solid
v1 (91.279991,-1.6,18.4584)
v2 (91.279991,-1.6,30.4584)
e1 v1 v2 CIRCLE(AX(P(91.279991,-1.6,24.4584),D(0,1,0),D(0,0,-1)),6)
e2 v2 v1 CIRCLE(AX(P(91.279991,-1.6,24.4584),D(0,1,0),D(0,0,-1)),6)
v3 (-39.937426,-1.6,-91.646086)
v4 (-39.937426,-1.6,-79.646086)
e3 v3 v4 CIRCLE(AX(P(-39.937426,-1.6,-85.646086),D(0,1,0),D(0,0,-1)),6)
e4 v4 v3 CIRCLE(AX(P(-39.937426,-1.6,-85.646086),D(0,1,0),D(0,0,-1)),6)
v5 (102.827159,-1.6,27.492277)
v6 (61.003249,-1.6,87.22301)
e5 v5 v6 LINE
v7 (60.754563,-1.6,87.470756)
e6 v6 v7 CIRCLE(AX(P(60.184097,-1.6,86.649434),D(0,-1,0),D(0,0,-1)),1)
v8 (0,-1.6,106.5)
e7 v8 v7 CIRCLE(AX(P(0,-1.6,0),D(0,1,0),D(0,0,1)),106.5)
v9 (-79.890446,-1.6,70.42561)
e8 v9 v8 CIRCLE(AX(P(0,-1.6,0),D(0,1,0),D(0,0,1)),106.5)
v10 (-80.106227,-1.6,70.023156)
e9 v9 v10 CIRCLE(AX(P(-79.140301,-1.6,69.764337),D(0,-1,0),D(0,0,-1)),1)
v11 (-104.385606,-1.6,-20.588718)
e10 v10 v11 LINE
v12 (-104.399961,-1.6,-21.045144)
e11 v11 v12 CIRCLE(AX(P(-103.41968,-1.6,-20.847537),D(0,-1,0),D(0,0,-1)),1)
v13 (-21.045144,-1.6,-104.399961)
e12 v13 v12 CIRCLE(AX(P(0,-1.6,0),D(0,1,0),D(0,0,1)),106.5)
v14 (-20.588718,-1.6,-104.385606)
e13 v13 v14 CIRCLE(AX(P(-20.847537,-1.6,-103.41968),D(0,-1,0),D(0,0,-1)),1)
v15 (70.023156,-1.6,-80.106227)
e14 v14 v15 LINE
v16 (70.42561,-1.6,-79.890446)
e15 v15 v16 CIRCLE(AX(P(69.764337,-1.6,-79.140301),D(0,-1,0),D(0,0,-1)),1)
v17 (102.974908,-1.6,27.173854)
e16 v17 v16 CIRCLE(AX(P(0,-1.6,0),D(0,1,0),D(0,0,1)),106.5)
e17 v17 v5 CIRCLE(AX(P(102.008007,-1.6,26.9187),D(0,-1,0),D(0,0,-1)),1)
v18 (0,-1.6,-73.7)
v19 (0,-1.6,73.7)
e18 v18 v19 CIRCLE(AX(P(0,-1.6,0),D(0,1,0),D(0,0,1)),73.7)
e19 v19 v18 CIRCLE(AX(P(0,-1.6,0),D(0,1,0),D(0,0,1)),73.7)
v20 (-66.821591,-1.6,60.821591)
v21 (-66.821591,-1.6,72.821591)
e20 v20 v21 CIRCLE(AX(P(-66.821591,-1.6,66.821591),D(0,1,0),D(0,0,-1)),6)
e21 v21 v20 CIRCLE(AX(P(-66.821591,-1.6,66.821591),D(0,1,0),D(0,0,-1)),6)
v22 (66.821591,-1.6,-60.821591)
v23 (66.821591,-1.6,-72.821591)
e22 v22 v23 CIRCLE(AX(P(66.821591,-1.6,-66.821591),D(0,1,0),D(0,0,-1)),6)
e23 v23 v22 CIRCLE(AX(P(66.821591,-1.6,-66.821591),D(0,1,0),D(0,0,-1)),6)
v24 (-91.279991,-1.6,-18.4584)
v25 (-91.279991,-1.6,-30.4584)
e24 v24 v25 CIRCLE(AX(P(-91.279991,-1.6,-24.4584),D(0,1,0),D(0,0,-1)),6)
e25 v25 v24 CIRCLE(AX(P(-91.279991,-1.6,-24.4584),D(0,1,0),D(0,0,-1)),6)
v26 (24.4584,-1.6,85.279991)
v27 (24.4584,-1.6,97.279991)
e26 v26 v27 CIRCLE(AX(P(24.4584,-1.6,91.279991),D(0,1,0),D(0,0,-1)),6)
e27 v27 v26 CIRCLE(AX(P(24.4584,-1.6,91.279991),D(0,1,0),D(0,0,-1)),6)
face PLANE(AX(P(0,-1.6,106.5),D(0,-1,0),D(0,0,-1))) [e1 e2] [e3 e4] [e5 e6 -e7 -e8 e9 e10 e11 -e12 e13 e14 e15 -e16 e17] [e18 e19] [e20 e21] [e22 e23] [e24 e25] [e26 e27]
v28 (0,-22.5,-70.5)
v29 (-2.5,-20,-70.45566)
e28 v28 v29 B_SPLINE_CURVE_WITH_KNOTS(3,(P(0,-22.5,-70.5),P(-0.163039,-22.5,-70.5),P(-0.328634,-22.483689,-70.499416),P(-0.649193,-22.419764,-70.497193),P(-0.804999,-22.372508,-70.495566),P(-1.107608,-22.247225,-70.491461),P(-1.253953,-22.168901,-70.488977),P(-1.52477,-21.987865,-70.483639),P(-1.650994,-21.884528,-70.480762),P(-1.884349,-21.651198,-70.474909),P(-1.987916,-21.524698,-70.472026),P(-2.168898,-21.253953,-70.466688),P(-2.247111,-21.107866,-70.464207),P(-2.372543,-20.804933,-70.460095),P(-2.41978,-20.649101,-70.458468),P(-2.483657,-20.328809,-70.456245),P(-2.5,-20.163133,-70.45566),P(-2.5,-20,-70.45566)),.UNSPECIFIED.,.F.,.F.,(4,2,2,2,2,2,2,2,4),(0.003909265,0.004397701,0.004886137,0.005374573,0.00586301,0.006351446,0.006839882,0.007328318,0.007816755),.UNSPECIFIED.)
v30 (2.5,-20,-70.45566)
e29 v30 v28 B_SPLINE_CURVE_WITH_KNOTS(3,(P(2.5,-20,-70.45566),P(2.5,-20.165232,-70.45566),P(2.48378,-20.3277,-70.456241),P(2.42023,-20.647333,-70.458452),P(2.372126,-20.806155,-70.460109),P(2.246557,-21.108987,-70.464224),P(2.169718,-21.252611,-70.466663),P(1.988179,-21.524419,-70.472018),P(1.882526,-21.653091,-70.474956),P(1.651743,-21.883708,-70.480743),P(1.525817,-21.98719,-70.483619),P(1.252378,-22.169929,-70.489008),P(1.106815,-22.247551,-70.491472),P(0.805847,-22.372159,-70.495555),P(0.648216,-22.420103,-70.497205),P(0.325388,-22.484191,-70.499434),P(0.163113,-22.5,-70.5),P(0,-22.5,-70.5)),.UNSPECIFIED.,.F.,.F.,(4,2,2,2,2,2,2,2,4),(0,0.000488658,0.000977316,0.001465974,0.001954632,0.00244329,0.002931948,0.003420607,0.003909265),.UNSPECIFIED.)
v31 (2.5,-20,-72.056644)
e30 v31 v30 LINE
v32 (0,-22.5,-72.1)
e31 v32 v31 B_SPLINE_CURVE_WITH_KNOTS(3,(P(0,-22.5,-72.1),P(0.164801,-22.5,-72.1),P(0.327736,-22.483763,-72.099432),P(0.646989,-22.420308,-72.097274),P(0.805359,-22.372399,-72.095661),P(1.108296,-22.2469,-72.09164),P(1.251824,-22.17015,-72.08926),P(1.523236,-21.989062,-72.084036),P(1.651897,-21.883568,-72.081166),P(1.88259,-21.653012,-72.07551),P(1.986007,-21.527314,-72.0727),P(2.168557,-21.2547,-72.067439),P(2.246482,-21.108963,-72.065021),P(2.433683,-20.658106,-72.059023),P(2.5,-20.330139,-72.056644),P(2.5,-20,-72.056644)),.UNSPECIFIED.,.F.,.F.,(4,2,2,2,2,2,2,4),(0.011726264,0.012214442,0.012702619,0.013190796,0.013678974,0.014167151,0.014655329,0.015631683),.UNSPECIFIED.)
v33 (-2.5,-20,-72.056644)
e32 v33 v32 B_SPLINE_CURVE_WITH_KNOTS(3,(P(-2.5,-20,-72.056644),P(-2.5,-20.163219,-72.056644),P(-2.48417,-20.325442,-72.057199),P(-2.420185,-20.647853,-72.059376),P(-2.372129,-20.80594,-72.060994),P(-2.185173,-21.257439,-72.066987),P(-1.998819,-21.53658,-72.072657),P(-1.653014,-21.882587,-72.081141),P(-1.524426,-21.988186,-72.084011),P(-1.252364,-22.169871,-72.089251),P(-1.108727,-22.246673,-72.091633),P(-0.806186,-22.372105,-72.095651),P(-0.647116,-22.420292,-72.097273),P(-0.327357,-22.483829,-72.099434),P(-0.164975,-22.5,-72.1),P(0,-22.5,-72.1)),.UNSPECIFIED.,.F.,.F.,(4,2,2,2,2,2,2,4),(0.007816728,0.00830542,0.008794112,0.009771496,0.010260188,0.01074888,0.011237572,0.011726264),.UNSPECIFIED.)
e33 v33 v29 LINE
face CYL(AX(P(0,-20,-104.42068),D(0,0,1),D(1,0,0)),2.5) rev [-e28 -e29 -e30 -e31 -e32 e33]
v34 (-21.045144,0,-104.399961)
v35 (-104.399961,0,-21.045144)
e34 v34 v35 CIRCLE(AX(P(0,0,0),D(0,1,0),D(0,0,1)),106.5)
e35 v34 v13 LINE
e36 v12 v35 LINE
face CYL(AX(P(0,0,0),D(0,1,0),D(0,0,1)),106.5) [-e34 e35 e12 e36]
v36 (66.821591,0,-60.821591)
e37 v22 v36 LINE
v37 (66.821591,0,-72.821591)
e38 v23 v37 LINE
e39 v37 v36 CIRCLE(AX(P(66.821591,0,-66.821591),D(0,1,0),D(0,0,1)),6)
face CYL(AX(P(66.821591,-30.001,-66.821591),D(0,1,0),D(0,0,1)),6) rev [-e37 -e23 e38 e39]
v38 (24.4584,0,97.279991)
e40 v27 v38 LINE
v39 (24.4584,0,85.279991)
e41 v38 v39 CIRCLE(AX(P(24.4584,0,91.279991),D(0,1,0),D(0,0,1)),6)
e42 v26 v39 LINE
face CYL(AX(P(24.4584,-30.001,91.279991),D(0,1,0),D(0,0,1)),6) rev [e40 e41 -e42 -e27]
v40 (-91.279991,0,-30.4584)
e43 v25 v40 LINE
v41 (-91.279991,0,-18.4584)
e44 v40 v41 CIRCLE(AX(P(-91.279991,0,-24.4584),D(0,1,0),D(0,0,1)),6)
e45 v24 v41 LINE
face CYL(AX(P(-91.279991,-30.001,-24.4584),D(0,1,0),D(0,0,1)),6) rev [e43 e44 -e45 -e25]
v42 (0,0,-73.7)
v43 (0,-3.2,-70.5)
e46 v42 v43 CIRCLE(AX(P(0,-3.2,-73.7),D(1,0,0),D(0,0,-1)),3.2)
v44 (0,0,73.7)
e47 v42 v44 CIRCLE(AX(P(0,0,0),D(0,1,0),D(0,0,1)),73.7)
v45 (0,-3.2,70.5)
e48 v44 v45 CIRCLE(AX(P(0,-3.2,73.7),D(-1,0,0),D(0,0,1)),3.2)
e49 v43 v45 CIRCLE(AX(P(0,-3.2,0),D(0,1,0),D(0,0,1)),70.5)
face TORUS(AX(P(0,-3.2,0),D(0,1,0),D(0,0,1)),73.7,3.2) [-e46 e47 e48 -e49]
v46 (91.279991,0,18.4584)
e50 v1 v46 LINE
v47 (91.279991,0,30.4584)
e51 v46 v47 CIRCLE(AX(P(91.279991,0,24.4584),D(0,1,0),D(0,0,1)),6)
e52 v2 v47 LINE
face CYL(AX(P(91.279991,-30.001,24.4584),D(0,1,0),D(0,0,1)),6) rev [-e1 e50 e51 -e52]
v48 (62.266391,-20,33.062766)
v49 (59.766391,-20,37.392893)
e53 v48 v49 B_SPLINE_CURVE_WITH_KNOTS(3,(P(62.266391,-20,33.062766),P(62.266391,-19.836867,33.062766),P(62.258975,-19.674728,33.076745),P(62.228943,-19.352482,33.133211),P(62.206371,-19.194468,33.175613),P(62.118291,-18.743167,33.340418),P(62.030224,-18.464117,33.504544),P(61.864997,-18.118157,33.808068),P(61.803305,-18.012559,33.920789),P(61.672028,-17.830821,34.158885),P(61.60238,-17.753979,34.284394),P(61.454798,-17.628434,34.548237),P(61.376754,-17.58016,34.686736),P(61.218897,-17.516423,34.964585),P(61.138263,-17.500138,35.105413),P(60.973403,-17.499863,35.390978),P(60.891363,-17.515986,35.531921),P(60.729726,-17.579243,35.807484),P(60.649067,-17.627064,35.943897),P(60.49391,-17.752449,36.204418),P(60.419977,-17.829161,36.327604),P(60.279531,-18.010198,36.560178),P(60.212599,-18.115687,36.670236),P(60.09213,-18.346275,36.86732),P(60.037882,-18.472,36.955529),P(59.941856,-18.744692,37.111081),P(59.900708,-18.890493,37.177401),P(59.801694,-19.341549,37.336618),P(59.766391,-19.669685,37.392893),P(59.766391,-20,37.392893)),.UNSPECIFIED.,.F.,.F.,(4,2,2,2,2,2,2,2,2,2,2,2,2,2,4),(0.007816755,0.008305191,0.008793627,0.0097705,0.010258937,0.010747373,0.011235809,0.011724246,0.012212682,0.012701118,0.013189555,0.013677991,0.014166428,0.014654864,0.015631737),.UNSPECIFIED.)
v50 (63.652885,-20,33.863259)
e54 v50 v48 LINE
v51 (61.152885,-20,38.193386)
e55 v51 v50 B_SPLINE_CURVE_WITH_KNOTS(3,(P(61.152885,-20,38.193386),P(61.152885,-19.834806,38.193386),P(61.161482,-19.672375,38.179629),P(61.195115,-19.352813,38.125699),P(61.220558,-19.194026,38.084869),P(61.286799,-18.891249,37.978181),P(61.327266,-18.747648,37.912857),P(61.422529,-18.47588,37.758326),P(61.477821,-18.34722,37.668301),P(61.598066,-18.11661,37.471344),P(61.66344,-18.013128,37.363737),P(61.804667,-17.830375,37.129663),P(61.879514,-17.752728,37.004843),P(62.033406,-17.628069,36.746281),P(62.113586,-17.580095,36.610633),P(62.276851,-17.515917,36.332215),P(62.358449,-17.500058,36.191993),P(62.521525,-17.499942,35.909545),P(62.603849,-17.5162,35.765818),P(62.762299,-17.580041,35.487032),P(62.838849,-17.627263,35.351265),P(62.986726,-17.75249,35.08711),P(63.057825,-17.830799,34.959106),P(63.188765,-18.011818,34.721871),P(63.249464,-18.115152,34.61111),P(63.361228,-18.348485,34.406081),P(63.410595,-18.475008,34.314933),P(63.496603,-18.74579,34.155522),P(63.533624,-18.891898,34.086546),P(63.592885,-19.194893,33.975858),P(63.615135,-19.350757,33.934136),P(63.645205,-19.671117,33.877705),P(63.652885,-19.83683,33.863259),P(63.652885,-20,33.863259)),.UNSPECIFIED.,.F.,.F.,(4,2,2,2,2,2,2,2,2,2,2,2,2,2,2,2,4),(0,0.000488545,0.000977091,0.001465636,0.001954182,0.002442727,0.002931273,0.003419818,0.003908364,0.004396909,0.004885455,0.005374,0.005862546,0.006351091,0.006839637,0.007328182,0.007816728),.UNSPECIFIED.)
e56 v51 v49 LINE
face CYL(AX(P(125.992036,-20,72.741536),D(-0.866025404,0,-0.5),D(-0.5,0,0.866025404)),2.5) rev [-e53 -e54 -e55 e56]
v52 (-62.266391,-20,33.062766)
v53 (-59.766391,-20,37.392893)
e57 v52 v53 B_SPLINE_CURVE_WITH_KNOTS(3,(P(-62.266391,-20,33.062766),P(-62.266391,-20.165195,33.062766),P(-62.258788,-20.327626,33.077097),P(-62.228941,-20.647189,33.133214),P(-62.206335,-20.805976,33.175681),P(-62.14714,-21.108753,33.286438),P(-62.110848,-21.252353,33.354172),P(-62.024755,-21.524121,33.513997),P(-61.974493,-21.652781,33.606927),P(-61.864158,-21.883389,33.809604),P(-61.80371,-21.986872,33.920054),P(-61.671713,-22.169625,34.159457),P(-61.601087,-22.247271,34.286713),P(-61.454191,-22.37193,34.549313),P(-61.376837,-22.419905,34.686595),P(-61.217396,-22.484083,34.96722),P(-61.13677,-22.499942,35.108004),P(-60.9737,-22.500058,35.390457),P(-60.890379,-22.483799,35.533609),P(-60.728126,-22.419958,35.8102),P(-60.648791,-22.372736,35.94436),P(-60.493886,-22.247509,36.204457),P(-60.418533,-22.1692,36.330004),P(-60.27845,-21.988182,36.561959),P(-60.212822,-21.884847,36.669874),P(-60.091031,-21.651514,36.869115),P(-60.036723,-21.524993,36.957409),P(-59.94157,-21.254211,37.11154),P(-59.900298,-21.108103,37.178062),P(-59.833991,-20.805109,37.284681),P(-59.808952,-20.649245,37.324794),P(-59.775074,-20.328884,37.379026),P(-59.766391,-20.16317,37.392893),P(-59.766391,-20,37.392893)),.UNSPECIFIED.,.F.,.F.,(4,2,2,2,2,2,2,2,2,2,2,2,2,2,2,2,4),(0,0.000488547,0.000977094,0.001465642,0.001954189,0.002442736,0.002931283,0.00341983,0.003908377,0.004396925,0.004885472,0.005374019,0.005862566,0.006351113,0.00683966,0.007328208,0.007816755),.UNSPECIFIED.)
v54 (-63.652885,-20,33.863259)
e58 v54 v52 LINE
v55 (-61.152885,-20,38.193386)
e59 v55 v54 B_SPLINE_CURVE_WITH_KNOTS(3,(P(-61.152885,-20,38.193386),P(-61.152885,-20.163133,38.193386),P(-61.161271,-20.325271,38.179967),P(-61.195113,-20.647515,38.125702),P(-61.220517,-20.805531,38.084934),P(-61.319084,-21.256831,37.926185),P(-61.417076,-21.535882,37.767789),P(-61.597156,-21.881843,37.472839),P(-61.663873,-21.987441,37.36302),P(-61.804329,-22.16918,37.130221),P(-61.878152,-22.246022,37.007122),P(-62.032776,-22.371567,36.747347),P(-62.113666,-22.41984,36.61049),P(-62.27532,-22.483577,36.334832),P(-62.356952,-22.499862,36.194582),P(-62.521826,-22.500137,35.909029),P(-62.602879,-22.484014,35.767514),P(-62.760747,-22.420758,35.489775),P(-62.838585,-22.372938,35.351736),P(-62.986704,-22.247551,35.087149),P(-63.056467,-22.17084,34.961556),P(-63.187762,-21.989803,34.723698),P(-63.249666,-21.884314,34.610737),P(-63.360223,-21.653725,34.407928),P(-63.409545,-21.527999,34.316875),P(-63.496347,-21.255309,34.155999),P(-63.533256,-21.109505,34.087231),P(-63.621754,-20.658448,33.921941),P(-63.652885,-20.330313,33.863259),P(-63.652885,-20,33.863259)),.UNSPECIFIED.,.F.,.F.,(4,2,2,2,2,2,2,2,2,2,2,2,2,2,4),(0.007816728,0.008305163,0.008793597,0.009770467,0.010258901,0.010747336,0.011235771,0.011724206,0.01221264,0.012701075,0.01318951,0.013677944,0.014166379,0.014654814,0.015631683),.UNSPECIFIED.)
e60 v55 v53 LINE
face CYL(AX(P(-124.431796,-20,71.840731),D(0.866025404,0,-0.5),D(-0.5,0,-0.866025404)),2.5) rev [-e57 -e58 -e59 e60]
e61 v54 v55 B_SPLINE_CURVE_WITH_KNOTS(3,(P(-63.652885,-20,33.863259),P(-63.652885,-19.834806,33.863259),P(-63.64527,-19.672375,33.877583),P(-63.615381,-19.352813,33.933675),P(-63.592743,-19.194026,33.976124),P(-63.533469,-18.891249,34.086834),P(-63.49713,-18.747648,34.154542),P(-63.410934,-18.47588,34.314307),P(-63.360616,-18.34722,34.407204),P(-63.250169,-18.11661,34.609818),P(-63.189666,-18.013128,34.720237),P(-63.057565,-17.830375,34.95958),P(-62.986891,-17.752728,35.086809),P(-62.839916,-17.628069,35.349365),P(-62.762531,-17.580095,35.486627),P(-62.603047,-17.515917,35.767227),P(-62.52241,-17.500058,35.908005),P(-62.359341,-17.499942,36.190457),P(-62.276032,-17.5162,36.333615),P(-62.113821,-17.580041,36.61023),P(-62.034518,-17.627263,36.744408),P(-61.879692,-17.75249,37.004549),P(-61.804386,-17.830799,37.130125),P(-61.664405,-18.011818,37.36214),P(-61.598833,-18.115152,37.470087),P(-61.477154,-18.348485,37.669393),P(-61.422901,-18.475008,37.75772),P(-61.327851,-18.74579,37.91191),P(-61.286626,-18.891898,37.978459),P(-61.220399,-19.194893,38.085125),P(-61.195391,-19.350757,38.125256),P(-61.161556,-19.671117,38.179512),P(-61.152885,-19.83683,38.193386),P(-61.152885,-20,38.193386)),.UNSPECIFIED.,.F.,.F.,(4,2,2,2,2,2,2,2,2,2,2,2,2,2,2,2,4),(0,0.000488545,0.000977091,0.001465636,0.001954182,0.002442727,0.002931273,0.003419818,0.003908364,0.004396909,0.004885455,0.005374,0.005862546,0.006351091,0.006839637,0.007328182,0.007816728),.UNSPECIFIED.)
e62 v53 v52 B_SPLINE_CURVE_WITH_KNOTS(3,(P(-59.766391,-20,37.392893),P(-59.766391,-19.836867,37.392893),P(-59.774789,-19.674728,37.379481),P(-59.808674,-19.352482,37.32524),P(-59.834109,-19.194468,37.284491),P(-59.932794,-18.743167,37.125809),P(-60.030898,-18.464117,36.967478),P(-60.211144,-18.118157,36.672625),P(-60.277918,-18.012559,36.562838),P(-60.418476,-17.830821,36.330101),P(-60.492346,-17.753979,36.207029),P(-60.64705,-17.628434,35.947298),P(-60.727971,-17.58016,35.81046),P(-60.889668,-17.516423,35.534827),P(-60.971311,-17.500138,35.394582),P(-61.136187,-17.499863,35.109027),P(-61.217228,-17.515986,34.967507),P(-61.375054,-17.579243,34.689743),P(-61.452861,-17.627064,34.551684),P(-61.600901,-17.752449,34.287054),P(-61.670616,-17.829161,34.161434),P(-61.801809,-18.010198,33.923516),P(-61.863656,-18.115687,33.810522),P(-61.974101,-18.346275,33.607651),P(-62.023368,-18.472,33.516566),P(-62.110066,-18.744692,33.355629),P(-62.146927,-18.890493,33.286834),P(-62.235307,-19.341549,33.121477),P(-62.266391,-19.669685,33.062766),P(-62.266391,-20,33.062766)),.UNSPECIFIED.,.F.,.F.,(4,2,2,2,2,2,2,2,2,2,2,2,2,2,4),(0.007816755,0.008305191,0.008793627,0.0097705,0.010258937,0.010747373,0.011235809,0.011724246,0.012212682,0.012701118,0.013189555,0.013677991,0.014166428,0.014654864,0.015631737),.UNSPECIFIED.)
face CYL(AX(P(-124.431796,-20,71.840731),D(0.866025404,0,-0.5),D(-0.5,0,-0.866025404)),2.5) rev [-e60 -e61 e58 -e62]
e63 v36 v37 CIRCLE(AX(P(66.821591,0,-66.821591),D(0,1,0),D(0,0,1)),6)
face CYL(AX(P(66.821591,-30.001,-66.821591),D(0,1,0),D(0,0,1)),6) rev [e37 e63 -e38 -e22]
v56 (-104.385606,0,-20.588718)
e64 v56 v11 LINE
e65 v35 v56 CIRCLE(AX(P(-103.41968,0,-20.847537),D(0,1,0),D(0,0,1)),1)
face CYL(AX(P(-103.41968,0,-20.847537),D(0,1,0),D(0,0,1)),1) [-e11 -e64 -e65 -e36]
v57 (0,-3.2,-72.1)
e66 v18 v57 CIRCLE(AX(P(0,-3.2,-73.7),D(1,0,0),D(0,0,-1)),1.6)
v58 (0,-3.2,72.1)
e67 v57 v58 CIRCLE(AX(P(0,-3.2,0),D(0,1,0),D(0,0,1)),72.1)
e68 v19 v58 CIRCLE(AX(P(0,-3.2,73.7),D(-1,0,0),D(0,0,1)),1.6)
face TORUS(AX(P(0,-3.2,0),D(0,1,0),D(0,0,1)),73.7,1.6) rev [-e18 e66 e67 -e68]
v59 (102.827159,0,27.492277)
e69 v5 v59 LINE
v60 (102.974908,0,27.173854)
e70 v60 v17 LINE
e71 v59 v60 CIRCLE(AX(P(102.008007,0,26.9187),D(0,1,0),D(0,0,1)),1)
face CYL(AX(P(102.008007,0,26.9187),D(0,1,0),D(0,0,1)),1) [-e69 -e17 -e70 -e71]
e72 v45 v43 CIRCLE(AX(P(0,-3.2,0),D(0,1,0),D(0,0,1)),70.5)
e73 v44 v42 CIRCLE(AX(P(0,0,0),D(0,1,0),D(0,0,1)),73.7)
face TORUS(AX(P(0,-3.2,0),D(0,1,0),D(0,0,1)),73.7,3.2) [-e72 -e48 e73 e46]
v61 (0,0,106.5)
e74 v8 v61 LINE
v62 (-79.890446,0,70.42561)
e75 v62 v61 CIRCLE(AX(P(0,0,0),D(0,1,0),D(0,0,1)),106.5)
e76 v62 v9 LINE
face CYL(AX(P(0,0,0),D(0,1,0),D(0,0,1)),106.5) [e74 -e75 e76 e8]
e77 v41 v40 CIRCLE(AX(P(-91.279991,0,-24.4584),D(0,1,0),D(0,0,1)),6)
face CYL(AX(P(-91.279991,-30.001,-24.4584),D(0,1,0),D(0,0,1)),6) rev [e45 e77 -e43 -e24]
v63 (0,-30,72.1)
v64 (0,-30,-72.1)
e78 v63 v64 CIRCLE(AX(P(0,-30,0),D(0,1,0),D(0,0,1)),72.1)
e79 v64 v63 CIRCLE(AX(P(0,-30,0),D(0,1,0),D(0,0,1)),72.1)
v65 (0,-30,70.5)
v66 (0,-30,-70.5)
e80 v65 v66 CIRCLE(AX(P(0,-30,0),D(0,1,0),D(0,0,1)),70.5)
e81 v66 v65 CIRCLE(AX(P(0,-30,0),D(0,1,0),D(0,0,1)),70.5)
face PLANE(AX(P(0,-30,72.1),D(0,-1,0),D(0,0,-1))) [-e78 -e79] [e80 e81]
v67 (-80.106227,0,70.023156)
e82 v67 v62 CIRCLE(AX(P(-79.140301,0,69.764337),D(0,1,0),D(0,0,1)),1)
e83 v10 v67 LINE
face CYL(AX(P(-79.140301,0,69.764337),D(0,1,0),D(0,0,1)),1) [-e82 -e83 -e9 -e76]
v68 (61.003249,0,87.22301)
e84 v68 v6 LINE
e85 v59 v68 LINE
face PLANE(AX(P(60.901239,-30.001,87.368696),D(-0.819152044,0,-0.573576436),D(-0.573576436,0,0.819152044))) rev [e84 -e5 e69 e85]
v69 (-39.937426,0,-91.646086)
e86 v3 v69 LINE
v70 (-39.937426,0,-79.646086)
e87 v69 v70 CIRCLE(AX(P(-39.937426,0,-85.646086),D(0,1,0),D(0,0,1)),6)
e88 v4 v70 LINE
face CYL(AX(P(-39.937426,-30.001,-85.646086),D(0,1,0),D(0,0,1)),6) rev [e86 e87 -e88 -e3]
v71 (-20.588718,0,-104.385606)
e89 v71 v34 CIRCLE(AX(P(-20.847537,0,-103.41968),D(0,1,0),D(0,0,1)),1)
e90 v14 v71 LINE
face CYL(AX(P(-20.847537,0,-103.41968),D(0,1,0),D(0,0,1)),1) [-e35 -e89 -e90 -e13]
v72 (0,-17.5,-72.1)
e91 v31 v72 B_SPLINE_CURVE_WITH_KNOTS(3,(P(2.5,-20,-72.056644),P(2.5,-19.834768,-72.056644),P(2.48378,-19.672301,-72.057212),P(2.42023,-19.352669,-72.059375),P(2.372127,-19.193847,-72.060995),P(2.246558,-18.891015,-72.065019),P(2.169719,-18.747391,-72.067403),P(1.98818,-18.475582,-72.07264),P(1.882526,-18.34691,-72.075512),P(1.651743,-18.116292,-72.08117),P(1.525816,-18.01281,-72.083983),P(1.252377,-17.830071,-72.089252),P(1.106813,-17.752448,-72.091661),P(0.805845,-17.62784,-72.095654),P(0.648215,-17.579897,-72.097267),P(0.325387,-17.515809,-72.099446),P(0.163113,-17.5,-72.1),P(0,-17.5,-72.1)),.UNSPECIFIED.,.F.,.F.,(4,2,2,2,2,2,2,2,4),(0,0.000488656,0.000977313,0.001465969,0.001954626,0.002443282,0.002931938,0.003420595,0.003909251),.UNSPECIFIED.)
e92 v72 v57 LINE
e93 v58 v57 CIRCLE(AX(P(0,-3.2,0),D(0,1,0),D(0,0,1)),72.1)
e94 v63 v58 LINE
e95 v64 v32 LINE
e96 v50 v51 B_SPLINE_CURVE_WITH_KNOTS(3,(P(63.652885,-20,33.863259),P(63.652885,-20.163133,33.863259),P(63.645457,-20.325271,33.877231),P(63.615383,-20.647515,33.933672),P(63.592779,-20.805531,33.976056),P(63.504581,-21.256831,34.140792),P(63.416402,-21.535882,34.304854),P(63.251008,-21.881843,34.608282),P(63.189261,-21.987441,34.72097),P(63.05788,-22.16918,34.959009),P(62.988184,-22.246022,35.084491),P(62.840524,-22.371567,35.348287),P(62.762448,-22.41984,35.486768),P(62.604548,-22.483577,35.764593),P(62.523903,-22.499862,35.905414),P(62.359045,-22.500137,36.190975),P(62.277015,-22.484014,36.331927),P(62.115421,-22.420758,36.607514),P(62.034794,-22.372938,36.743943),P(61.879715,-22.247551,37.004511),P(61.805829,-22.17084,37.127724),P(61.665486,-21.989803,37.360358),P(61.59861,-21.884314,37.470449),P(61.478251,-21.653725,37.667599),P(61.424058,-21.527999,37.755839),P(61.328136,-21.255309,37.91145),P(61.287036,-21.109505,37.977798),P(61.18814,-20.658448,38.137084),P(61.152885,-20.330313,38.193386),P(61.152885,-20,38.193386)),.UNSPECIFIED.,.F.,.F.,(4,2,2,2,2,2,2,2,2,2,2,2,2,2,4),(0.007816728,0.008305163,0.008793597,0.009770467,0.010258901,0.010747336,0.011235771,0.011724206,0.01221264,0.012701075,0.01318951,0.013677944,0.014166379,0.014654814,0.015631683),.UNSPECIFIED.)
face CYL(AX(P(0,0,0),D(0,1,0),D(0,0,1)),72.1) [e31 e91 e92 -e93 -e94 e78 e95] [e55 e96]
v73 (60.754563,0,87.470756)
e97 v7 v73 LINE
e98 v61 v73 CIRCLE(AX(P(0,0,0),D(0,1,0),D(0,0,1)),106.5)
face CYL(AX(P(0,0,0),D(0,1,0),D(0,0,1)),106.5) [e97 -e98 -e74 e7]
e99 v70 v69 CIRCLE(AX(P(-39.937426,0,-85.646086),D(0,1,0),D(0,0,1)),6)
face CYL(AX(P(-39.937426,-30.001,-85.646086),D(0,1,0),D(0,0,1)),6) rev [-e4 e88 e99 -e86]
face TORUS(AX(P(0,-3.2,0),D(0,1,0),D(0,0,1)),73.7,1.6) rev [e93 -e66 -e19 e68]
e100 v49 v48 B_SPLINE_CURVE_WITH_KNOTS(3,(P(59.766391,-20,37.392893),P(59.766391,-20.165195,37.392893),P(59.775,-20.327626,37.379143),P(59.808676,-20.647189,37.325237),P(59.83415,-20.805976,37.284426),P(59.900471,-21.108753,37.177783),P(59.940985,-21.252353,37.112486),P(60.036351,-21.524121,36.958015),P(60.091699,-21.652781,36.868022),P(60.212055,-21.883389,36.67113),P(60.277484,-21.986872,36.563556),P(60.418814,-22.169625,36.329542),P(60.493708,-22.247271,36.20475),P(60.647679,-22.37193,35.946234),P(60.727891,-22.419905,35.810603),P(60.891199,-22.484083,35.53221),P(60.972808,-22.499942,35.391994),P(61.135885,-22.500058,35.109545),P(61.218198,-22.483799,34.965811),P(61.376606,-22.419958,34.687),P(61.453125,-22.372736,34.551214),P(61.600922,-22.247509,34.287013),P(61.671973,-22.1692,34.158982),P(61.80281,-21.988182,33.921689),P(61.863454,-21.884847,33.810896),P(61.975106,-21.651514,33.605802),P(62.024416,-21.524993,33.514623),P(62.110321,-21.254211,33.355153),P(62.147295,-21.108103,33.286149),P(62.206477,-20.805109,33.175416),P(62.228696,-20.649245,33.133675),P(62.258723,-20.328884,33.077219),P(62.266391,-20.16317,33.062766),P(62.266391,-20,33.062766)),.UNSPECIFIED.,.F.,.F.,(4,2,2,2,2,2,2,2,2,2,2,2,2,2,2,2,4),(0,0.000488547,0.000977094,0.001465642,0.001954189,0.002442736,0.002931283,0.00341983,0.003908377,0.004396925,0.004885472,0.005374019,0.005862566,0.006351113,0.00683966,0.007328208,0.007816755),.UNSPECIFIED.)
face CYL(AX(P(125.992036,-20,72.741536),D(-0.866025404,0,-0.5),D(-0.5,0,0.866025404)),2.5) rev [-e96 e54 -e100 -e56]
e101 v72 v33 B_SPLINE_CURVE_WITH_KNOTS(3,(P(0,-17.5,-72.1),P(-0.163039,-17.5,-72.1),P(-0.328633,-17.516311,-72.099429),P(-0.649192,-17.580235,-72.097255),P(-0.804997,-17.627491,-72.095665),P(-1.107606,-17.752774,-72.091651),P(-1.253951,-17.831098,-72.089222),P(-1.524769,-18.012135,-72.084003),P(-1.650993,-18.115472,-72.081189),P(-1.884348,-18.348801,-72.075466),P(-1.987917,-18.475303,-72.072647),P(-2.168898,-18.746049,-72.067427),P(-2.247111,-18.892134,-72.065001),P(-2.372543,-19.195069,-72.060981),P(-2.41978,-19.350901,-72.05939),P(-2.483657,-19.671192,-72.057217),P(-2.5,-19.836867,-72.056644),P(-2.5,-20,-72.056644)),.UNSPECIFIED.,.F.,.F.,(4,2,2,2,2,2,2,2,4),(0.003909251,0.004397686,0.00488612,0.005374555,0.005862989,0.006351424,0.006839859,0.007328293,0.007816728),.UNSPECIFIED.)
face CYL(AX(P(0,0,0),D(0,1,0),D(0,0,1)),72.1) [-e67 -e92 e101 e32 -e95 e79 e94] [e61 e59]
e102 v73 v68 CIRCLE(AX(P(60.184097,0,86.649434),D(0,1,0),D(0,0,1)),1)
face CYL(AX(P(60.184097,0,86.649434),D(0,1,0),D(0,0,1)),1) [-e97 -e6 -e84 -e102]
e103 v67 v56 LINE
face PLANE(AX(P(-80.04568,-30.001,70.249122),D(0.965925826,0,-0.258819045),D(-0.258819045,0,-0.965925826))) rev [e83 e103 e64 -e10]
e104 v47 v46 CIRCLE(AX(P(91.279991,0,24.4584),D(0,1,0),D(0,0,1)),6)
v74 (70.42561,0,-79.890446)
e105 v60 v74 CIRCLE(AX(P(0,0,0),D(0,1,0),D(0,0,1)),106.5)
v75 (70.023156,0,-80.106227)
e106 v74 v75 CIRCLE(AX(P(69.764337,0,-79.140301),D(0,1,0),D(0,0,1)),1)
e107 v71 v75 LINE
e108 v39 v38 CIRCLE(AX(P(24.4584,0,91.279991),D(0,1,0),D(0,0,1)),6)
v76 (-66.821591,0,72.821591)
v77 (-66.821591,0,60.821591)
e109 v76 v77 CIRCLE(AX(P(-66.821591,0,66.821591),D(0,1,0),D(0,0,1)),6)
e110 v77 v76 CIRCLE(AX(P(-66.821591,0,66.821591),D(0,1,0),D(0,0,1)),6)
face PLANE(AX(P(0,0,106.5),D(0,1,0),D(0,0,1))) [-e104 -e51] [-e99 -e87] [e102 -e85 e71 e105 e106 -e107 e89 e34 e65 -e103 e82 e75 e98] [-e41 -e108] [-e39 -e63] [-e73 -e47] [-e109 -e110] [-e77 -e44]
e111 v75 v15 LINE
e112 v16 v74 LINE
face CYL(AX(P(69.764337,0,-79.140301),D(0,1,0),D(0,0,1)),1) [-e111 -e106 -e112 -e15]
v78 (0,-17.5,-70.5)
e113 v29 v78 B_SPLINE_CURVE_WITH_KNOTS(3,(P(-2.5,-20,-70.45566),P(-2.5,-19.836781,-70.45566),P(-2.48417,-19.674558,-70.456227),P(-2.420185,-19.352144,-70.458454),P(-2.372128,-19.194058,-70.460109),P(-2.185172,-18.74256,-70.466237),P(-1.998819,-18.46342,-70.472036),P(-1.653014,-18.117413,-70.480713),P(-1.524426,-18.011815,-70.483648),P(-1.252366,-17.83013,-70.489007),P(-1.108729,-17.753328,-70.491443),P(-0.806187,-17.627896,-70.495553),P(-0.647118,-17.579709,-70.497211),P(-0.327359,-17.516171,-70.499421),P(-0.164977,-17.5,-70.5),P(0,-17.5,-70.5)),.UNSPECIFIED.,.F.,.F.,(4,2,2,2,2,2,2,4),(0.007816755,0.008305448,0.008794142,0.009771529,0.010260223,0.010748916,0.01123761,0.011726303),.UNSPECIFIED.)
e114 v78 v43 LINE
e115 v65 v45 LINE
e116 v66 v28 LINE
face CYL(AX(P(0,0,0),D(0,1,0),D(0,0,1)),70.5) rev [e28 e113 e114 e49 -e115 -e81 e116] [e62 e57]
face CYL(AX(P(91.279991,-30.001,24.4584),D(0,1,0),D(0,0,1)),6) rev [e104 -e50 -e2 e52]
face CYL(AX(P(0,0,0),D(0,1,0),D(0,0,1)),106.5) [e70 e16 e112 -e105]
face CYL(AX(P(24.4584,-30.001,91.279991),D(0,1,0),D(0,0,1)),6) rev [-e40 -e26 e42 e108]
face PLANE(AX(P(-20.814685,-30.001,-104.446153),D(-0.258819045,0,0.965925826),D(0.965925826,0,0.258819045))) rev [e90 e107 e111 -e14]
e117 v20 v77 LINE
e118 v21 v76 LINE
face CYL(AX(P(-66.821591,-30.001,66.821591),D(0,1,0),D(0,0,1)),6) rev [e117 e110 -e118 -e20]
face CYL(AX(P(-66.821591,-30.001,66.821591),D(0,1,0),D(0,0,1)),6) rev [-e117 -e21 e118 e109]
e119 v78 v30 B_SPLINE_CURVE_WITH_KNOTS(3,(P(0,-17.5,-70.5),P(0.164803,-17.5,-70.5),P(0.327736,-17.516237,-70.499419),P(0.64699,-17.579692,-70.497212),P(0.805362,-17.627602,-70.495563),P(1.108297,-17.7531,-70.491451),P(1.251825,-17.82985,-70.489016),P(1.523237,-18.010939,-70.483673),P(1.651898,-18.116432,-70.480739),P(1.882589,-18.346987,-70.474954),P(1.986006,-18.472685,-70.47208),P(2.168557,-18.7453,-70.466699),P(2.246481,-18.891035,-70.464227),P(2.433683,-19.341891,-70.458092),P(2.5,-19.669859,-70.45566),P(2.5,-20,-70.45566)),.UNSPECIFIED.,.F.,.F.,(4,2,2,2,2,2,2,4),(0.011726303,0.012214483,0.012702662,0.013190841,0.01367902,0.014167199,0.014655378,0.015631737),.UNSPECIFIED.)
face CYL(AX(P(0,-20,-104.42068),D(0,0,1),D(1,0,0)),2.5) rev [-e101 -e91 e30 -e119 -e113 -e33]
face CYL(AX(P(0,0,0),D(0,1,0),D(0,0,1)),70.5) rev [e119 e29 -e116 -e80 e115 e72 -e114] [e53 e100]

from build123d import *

# Parameters (mm, degrees)
CUT_EXTRUDE1_REACH      = 155.572
SKETCH2_R               = 6
CUT_EXTRUDE2_REACH      = 155.572
FILLET1_R               = 1
CUT_EXTRUDE3_REACH      = 155.572
CUT_EXTRUDE3_END_RADIUS = 72.1
SKETCH4_R               = 2.5
CIRPATTERN1_COUNT       = 3


with BuildPart() as part:
    # Sketch1 → Revolve1 (revolve)
    with BuildSketch(Plane(origin=(0, 0, 0), x_dir=(0, 0, -1), z_dir=(1, 0, 0))):
        with BuildLine():
            Line((-106.5, 0), (-73.7, 0))
            ThreePointArc((-73.7, 0), (-71.4372583, -0.9372583), (-70.5, -3.2))
            Line((-70.5, -3.2), (-70.5, -30))
            Line((-70.5, -30), (-72.1, -30))
            Line((-72.1, -30), (-72.1, -3.2))
            ThreePointArc((-72.1, -3.2), (-72.56862915, -2.06862915), (-73.7, -1.6))
            Line((-73.7, -1.6), (-106.5, -1.6))
            Line((-106.5, -1.6), (-106.5, 0))
        make_face()
    revolve(axis=Axis((0, 0, 0), (0, -1, 0)))

    # Sketch2 → Cut-Extrude1 (cut, up to next)
    with BuildSketch(Plane(origin=(0, 0, 0), x_dir=(1, 0, 0), z_dir=(0, 1, 0)), mode=Mode.PRIVATE) as cut_extrude1_sk1:
        with Locations(Location((-91.279990584, 24.458399762, 0), (0, 0, 270))):
            Circle(SKETCH2_R)
    cut_extrude1_tool1 = extrude(cut_extrude1_sk1.sketch, amount=-CUT_EXTRUDE1_REACH, mode=Mode.PRIVATE) & part.part
    # Sketch2 → Cut-Extrude1 (cut, up to next)
    with BuildSketch(Plane(origin=(0, 0, 0), x_dir=(1, 0, 0), z_dir=(0, 1, 0)), mode=Mode.PRIVATE) as cut_extrude1_sk2:
        with Locations(Location((-39.937425734, 85.646085875, 0), (0, 0, 270))):
            Circle(SKETCH2_R)
    cut_extrude1_tool2 = extrude(cut_extrude1_sk2.sketch, amount=-CUT_EXTRUDE1_REACH, mode=Mode.PRIVATE) & part.part
    # Sketch2 → Cut-Extrude1 (cut, up to next)
    with BuildSketch(Plane(origin=(0, 0, 0), x_dir=(1, 0, 0), z_dir=(0, 1, 0)), mode=Mode.PRIVATE) as cut_extrude1_sk3:
        with Locations(Location((66.821590822, 66.821590822, 0), (0, 0, 270))):
            Circle(SKETCH2_R)
    cut_extrude1_tool3 = extrude(cut_extrude1_sk3.sketch, amount=-CUT_EXTRUDE1_REACH, mode=Mode.PRIVATE) & part.part
    # Sketch2 → Cut-Extrude1 (cut, up to next)
    with BuildSketch(Plane(origin=(0, 0, 0), x_dir=(1, 0, 0), z_dir=(0, 1, 0)), mode=Mode.PRIVATE) as cut_extrude1_sk4:
        with Locations(Location((91.279990584, -24.458399762, 0), (0, 0, 270))):
            Circle(SKETCH2_R)
    cut_extrude1_tool4 = extrude(cut_extrude1_sk4.sketch, amount=-CUT_EXTRUDE1_REACH, mode=Mode.PRIVATE) & part.part
    # Sketch2 → Cut-Extrude1 (cut, up to next)
    with BuildSketch(Plane(origin=(0, 0, 0), x_dir=(1, 0, 0), z_dir=(0, 1, 0)), mode=Mode.PRIVATE) as cut_extrude1_sk5:
        with Locations(Location((24.458399762, -91.279990584, 0), (0, 0, 270))):
            Circle(SKETCH2_R)
    cut_extrude1_tool5 = extrude(cut_extrude1_sk5.sketch, amount=-CUT_EXTRUDE1_REACH, mode=Mode.PRIVATE) & part.part
    # Sketch2 → Cut-Extrude1 (cut, up to next)
    with BuildSketch(Plane(origin=(0, 0, 0), x_dir=(1, 0, 0), z_dir=(0, 1, 0)), mode=Mode.PRIVATE) as cut_extrude1_sk6:
        with Locations(Location((-66.821590822, -66.821590822, 0), (0, 0, 270))):
            Circle(SKETCH2_R)
    cut_extrude1_tool6 = extrude(cut_extrude1_sk6.sketch, amount=-CUT_EXTRUDE1_REACH, mode=Mode.PRIVATE) & part.part
    add(cut_extrude1_tool1.solids().sort_by_distance((-91.279991, 0, -24.4584))[0], mode=Mode.SUBTRACT)
    add(cut_extrude1_tool2.solids().sort_by_distance((-39.937426, 0, -85.646086))[0], mode=Mode.SUBTRACT)
    add(cut_extrude1_tool3.solids().sort_by_distance((66.821591, 0, -66.821591))[0], mode=Mode.SUBTRACT)
    add(cut_extrude1_tool4.solids().sort_by_distance((91.279991, 0, 24.4584))[0], mode=Mode.SUBTRACT)
    add(cut_extrude1_tool5.solids().sort_by_distance((24.4584, 0, 91.279991))[0], mode=Mode.SUBTRACT)
    add(cut_extrude1_tool6.solids().sort_by_distance((-66.821591, 0, 66.821591))[0], mode=Mode.SUBTRACT)

    # Sketch3 → Cut-Extrude2 (cut, up to next)
    with BuildSketch(Plane(origin=(0, 0, 0), x_dir=(1, 0, 0), z_dir=(0, 1, 0)), mode=Mode.PRIVATE) as cut_extrude2_sk1:
        with BuildLine():
            Line((-80.045679675, -70.249122168), (-104.446153146, 20.814684553))
            ThreePointArc((-104.446153146, 20.814684553), (-102.8711005, -27.564228303), (-80.045679675, -70.249122168))
        make_face()
    cut_extrude2_tool1 = extrude(cut_extrude2_sk1.sketch, amount=-CUT_EXTRUDE2_REACH, mode=Mode.PRIVATE) & part.part
    # Sketch3 → Cut-Extrude2 (cut, up to next)
    with BuildSketch(Plane(origin=(0, 0, 0), x_dir=(1, 0, 0), z_dir=(0, 1, 0)), mode=Mode.PRIVATE) as cut_extrude2_sk2:
        with BuildLine():
            Line((-20.814684553, 104.446153146), (70.249122168, 80.045679675))
            ThreePointArc((70.249122168, 80.045679675), (27.564228303, 102.8711005), (-20.814684553, 104.446153146))
        make_face()
    cut_extrude2_tool2 = extrude(cut_extrude2_sk2.sketch, amount=-CUT_EXTRUDE2_REACH, mode=Mode.PRIVATE) & part.part
    # Sketch3 → Cut-Extrude2 (cut, up to next)
    with BuildSketch(Plane(origin=(0, 0, 0), x_dir=(1, 0, 0), z_dir=(0, 1, 0)), mode=Mode.PRIVATE) as cut_extrude2_sk3:
        with BuildLine():
            Line((60.901239279, -87.368696077), (102.929169579, -27.346591193))
            ThreePointArc((102.929169579, -27.346591193), (87.239692717, -61.085890471), (60.901239279, -87.368696077))
        make_face()
    cut_extrude2_tool3 = extrude(cut_extrude2_sk3.sketch, amount=-CUT_EXTRUDE2_REACH, mode=Mode.PRIVATE) & part.part
    add(cut_extrude2_tool1.solids().sort_by_distance((-96.515383, 0, 25.861219))[0], mode=Mode.SUBTRACT)
    add(cut_extrude2_tool2.solids().sort_by_distance((25.861219, 0, -96.515383))[0], mode=Mode.SUBTRACT)
    add(cut_extrude2_tool3.solids().sort_by_distance((84.050671, 0, 58.852913))[0], mode=Mode.SUBTRACT)

    # Fillet1
    fillet1_edges = [part.edges().sort_by_distance(p)[0] for p in [
        (-80.045679675, -0.8, 70.249122168),
        (-104.446153146, -0.8, -20.814684553),
        (-20.814684553, -0.8, -104.446153146),
        (70.249122168, -0.8, -80.045679675),
        (102.929169579, -0.8, 27.346591193),
        (60.901239279, -0.8, 87.368696077),
    ]]
    fillet(fillet1_edges, radius=FILLET1_R)

    # Cut-Extrude3: up to this cylinder (the profile starts inside it)
    cut_extrude3_end = Plane(origin=(0, -20, 0), z_dir=(0, 1, 0)) * Cylinder(CUT_EXTRUDE3_END_RADIUS, 456.344, mode=Mode.PRIVATE)
    # Sketch4 → Cut-Extrude3 (cut, up to the surface)
    with BuildSketch(Plane.XY, mode=Mode.PRIVATE) as cut_extrude3_sk1:
        with Locations((0, -20)):
            Circle(SKETCH4_R)
    cut_extrude3_tool1 = extrude(cut_extrude3_sk1.sketch, amount=-CUT_EXTRUDE3_REACH, mode=Mode.PRIVATE) & cut_extrude3_end
    cut_extrude3 = cut_extrude3_tool1.solids().sort_by_distance((0, -20, 0))[0]
    add(cut_extrude3, mode=Mode.SUBTRACT)

    # CirPattern1: Cut-Extrude3 ×3 about axis
    cirpattern1_axis = Axis((0, -30, 0), (0, 1, 0))
    for i in range(1, CIRPATTERN1_COUNT):
        add(cut_extrude3.rotate(cirpattern1_axis, i * 360 / CIRPATTERN1_COUNT), mode=Mode.SUBTRACT)


solid = part.part
